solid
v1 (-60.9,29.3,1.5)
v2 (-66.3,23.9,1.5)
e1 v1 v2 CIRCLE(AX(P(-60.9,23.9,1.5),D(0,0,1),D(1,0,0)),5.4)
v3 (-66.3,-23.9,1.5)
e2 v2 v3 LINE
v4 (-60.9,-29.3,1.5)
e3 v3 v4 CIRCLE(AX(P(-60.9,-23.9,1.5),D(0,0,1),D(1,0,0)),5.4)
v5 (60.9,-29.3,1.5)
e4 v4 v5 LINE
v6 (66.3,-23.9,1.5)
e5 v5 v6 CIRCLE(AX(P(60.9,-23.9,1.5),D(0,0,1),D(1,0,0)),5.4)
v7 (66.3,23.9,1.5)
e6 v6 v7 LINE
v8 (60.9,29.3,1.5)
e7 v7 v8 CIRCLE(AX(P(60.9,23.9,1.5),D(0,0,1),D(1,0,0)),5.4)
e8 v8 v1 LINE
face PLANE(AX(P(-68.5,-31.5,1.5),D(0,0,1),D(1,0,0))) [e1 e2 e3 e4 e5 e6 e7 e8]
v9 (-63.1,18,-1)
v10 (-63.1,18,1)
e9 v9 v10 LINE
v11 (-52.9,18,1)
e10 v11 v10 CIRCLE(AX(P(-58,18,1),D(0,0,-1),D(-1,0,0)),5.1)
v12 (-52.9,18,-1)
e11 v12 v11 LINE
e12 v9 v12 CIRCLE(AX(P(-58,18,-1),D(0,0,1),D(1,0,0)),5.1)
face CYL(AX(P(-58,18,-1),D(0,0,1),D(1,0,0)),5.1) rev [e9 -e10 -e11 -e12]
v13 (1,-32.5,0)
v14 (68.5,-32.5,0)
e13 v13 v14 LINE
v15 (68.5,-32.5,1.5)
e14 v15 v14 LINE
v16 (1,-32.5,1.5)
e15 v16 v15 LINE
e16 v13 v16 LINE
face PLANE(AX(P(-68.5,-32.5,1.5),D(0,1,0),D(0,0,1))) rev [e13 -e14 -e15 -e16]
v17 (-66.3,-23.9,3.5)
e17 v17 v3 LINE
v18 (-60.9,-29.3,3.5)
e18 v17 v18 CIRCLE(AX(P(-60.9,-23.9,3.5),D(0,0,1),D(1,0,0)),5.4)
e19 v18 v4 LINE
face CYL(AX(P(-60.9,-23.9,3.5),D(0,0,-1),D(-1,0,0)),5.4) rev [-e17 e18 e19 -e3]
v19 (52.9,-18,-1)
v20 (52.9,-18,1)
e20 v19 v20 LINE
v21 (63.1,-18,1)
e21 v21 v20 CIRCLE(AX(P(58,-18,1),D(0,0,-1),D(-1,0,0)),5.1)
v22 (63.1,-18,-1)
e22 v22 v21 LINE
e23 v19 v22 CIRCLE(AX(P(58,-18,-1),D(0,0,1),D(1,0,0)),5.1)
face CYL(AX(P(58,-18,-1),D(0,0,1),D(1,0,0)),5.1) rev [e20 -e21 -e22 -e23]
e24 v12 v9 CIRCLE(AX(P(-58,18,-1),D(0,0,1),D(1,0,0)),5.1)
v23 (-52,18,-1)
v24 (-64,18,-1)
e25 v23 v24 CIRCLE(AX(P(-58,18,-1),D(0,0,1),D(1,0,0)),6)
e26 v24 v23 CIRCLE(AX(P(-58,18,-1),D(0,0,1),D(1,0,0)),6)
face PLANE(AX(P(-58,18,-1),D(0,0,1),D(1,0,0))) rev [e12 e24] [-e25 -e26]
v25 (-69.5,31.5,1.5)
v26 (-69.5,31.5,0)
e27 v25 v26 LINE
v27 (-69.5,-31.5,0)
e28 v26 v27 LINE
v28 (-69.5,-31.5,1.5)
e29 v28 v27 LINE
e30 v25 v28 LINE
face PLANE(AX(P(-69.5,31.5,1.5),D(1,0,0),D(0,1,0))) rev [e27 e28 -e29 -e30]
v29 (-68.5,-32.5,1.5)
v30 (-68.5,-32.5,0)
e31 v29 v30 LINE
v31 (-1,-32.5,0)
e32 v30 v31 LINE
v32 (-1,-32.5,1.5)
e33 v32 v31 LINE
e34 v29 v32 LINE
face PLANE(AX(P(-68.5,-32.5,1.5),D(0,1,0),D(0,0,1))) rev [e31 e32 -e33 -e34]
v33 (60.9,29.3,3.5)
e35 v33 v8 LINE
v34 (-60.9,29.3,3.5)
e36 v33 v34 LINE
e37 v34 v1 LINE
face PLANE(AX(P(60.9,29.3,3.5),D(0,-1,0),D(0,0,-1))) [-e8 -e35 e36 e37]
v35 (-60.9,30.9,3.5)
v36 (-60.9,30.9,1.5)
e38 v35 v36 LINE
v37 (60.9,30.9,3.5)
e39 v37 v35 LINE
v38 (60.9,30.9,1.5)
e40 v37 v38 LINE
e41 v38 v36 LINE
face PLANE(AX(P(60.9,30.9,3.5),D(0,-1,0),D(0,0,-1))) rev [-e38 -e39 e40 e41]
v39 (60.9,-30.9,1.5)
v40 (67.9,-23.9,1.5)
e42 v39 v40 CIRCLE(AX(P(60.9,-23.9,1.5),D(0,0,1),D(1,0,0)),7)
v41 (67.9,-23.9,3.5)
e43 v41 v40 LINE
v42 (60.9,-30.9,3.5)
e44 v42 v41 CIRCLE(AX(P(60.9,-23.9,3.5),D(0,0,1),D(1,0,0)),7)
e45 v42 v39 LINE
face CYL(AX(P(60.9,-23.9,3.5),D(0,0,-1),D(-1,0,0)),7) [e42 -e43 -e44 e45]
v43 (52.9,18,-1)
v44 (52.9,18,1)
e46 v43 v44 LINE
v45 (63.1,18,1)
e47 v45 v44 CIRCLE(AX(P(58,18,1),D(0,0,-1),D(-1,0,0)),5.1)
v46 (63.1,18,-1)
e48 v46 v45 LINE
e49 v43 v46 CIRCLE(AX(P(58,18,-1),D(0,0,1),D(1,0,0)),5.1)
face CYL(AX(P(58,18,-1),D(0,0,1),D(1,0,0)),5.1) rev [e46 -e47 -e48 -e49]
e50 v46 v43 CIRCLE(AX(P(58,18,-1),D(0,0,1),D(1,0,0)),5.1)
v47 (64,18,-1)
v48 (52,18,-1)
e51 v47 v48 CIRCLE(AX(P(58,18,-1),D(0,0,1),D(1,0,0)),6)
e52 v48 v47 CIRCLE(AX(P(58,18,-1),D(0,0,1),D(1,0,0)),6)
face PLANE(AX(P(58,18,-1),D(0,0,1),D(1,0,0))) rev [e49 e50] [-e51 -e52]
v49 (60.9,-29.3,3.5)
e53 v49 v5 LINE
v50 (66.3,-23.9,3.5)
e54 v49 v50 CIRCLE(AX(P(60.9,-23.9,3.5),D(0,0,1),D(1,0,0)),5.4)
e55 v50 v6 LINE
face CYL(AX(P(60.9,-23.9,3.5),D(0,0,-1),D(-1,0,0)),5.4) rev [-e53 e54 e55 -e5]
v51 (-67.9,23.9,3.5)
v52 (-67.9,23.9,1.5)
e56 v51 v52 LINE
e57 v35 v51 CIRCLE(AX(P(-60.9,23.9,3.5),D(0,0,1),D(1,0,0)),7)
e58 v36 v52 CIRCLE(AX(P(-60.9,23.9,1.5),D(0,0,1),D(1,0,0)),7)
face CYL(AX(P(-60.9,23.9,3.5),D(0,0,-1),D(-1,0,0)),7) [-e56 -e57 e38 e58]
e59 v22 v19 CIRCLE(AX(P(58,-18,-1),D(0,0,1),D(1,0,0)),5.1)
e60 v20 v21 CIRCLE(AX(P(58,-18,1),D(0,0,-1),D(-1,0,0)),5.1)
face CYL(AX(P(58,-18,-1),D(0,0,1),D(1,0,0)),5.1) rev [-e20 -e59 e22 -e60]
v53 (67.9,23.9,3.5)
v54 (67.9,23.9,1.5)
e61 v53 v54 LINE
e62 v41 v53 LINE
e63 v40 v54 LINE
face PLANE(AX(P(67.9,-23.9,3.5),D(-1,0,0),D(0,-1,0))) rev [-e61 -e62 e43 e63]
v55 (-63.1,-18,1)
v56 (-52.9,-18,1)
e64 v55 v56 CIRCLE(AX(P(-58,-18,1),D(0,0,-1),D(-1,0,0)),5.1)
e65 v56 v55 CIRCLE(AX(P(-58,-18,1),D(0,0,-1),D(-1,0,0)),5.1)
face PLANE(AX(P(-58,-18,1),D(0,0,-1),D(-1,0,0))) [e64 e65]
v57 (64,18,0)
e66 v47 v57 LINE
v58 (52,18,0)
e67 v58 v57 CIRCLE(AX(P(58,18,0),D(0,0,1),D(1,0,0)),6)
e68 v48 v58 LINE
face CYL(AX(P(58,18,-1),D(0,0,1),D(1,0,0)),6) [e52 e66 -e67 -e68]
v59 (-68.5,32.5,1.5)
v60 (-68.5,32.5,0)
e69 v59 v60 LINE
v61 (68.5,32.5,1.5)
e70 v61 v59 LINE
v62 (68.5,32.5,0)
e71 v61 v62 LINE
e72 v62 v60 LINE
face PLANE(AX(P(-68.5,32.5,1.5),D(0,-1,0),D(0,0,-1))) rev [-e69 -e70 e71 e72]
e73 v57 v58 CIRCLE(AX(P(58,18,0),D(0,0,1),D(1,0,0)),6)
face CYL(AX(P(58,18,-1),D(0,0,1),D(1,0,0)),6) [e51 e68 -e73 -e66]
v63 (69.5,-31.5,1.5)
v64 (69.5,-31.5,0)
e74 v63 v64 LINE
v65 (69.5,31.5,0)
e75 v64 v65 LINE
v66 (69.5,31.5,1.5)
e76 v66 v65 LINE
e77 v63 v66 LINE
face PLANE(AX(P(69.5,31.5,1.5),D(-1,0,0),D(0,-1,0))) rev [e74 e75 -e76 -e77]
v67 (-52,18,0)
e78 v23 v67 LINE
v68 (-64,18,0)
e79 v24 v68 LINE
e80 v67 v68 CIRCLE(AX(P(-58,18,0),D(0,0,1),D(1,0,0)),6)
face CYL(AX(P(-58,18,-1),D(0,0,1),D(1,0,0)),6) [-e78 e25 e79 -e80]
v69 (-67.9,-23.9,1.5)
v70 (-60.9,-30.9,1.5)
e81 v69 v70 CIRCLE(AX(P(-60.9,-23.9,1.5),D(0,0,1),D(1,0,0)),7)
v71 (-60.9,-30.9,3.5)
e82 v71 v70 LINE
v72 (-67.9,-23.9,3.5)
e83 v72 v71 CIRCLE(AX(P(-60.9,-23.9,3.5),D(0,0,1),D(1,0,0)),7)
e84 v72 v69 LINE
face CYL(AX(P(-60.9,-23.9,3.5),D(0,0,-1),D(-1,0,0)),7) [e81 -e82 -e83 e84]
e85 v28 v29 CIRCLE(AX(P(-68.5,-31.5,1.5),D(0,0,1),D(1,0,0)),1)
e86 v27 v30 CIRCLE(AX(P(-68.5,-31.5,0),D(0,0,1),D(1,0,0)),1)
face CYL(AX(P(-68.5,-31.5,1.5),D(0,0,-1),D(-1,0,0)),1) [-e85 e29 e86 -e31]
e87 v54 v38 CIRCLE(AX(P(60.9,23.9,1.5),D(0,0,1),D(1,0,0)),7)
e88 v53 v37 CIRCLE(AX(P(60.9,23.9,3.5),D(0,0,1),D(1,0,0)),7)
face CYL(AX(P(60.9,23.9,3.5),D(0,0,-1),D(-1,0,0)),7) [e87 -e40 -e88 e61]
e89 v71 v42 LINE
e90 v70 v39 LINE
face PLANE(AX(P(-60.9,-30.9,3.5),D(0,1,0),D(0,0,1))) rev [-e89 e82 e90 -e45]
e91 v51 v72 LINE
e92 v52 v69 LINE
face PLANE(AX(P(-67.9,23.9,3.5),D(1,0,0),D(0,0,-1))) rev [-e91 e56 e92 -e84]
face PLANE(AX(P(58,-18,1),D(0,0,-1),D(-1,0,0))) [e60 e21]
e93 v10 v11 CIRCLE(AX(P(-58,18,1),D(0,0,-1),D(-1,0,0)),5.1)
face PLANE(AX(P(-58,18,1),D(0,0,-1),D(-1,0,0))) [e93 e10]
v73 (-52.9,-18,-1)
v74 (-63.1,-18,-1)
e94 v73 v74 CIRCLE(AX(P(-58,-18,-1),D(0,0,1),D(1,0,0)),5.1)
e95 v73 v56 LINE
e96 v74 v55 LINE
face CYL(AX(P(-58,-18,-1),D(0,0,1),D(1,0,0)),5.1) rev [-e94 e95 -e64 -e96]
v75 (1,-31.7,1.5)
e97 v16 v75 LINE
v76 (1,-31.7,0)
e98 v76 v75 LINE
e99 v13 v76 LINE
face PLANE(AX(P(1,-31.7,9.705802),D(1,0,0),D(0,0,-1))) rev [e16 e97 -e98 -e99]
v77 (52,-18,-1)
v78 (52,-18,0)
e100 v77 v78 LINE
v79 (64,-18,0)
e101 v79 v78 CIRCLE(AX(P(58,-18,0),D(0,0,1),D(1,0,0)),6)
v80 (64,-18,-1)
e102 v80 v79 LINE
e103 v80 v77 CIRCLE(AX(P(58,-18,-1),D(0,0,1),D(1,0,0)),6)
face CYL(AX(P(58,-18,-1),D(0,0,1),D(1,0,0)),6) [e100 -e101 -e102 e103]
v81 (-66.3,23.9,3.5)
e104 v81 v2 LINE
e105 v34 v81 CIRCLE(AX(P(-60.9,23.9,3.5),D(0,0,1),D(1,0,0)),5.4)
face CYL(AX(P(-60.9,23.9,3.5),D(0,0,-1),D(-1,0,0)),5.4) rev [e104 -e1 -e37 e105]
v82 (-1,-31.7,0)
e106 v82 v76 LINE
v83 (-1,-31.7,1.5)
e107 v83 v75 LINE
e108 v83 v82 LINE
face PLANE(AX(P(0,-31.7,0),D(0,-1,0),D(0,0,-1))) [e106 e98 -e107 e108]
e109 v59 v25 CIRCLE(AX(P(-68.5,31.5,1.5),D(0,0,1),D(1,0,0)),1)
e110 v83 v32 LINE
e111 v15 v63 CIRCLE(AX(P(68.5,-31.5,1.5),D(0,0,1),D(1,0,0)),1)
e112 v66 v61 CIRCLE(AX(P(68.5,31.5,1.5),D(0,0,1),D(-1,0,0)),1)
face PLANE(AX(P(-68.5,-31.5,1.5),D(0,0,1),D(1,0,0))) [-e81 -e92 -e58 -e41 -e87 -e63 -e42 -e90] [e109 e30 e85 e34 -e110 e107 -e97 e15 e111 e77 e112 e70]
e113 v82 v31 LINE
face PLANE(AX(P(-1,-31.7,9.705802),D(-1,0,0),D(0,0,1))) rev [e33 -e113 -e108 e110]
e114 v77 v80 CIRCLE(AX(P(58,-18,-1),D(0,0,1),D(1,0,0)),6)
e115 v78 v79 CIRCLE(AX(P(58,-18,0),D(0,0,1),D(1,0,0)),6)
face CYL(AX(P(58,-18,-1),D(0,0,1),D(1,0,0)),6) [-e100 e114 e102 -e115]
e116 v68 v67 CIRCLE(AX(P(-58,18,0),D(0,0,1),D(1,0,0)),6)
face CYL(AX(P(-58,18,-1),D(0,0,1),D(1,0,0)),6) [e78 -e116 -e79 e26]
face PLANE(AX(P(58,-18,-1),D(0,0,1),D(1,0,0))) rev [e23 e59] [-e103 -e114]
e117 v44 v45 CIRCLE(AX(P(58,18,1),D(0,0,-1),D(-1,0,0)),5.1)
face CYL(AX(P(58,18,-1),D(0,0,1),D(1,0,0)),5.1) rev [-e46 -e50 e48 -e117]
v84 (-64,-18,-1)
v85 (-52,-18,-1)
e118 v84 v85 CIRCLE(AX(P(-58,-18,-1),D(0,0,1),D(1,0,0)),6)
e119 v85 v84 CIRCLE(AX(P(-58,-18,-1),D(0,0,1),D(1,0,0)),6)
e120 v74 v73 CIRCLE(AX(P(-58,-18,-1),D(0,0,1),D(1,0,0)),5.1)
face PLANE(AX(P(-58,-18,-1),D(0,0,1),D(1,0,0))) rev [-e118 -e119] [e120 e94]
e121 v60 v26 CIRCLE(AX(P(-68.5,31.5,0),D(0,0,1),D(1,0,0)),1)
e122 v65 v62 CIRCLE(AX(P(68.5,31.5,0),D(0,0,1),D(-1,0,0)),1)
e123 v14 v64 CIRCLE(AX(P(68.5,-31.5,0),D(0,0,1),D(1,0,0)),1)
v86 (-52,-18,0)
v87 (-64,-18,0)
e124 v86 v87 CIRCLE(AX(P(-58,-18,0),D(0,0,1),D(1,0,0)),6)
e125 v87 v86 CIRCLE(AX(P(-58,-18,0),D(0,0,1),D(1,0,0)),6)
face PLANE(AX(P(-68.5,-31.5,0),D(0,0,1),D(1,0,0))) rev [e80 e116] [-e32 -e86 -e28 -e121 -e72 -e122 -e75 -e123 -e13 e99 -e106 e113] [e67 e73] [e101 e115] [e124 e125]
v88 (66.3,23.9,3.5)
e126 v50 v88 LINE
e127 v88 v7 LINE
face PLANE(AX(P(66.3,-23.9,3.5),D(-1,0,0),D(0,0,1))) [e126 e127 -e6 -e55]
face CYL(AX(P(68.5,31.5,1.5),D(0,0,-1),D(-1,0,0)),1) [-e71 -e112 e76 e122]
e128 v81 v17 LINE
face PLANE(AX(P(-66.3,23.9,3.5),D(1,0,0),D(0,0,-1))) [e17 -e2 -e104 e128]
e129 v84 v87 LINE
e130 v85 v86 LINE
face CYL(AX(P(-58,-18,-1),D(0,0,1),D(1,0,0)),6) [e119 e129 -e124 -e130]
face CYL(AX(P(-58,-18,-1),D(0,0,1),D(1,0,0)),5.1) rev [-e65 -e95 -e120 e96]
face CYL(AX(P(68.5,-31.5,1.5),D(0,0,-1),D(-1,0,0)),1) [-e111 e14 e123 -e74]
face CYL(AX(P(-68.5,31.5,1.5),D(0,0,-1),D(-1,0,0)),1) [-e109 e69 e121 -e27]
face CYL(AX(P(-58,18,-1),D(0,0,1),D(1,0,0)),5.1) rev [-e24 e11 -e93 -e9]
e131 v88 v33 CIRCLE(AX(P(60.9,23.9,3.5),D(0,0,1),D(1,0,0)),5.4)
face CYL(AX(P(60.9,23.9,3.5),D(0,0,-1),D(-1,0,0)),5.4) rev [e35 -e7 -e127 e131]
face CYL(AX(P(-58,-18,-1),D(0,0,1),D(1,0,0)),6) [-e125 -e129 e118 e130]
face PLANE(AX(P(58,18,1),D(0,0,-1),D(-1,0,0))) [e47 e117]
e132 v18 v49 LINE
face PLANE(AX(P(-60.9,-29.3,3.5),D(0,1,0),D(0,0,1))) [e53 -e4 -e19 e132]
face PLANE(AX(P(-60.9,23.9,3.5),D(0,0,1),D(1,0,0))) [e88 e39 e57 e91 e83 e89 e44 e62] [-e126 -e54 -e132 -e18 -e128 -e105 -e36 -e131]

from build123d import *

# Parameters (mm, degrees)
BOSS_EXTRUDE1_DEPTH = 1.5
BOSS_EXTRUDE2_START = -1.5
SKETCH2_R           = 6
SKETCH2_R_2         = 5.1
BOSS_EXTRUDE2_DEPTH = 1
BOSS_EXTRUDE3_DEPTH = 2
SKETCH7_W           = 2
SKETCH7_H           = 19.411603012
CUT_EXTRUDE3_DEPTH  = 0.8
CUT_EXTRUDE4_START  = -1
SKETCH8_R           = 5.1
CUT_EXTRUDE4_DEPTH  = 1


with BuildPart() as part:
    # Sketch1 → Boss-Extrude1 (new body)
    with BuildSketch(Plane.XY):
        with BuildLine():
            Line((-68.5, 32.5), (68.5, 32.5))
            ThreePointArc((68.5, 32.5), (69.207106781, 32.207106781), (69.5, 31.5))
            Line((69.5, 31.5), (69.5, -31.5))
            ThreePointArc((69.5, -31.5), (69.207106781, -32.207106781), (68.5, -32.5))
            Line((68.5, -32.5), (-68.5, -32.5))
            ThreePointArc((-68.5, -32.5), (-69.207106781, -32.207106781), (-69.5, -31.5))
            Line((-69.5, -31.5), (-69.5, 31.5))
            ThreePointArc((-69.5, 31.5), (-69.207106781, 32.207106781), (-68.5, 32.5))
        make_face()
    extrude(amount=BOSS_EXTRUDE1_DEPTH)

    # Sketch2 → Boss-Extrude2 (add)
    # profile 1 of 4: a face of its own
    with BuildSketch(Plane.XY.offset(1.5).offset(BOSS_EXTRUDE2_START)):
        with Locations((-58, 18)):
            Circle(SKETCH2_R)
        with Locations((-58, 18)):
            Circle(SKETCH2_R_2, mode=Mode.SUBTRACT)
    # profile 2 of 4: a face of its own
    with BuildSketch(Plane.XY.offset(1.5).offset(BOSS_EXTRUDE2_START)):
        with Locations((58, 18)):
            Circle(SKETCH2_R)
        with Locations((58, 18)):
            Circle(SKETCH2_R_2, mode=Mode.SUBTRACT)
    # profile 3 of 4: a face of its own
    with BuildSketch(Plane.XY.offset(1.5).offset(BOSS_EXTRUDE2_START)):
        with Locations((-58, -18)):
            Circle(SKETCH2_R)
        with Locations((-58, -18)):
            Circle(SKETCH2_R_2, mode=Mode.SUBTRACT)
    # profile 4 of 4: a face of its own
    with BuildSketch(Plane.XY.offset(1.5).offset(BOSS_EXTRUDE2_START)):
        with Locations((58, -18)):
            Circle(SKETCH2_R)
        with Locations((58, -18)):
            Circle(SKETCH2_R_2, mode=Mode.SUBTRACT)
    extrude(amount=-BOSS_EXTRUDE2_DEPTH)

    # Sketch3 → Boss-Extrude3 (add)
    with BuildSketch(Plane.XY.offset(1.5)):
        with BuildLine():
            Line((60.9, 30.9), (-60.9, 30.9))
            ThreePointArc((-60.9, 30.9), (-65.849747468, 28.849747468), (-67.9, 23.9))
            Line((-67.9, 23.9), (-67.9, -23.9))
            ThreePointArc((-67.9, -23.9), (-65.849747468, -28.849747468), (-60.9, -30.9))
            Line((-60.9, -30.9), (60.9, -30.9))
            ThreePointArc((60.9, -30.9), (65.849747468, -28.849747468), (67.9, -23.9))
            Line((67.9, -23.9), (67.9, 23.9))
            ThreePointArc((67.9, 23.9), (65.849747468, 28.849747468), (60.9, 30.9))
        make_face()
        with BuildLine():
            Line((60.9, 29.3), (-60.9, 29.3))
            ThreePointArc((-60.9, 29.3), (-64.718376618, 27.718376618), (-66.3, 23.9))
            Line((-66.3, 23.9), (-66.3, -23.9))
            ThreePointArc((-66.3, -23.9), (-64.718376618, -27.718376618), (-60.9, -29.3))
            Line((-60.9, -29.3), (60.9, -29.3))
            ThreePointArc((60.9, -29.3), (64.718376618, -27.718376618), (66.3, -23.9))
            Line((66.3, -23.9), (66.3, 23.9))
            ThreePointArc((66.3, 23.9), (64.718376618, 27.718376618), (60.9, 29.3))
        make_face(mode=Mode.SUBTRACT)
    extrude(amount=BOSS_EXTRUDE3_DEPTH)

    # Sketch7 → Cut-Extrude3 (cut)
    with BuildSketch(Plane(origin=(0, -32.5, 0), x_dir=(-1, 0, 0), z_dir=(0, -1, 0))):
        Rectangle(SKETCH7_W, SKETCH7_H)
    extrude(amount=-CUT_EXTRUDE3_DEPTH, mode=Mode.SUBTRACT)

    # Sketch8 → Cut-Extrude4 (cut)
    with BuildSketch(Plane(origin=(0, 0, 0), x_dir=(-1, 0, 0), z_dir=(0, 0, -1)).offset(CUT_EXTRUDE4_START)):
        with Locations(Location((-58, 18, 0), (0, 0, 180))):
            Circle(SKETCH8_R)
        with Locations(Location((58, 18, 0), (0, 0, 180))):
            Circle(SKETCH8_R)
        with Locations(Location((58, -18, 0), (0, 0, 180))):
            Circle(SKETCH8_R)
        with Locations(Location((-58, -18, 0), (0, 0, 180))):
            Circle(SKETCH8_R)
    extrude(amount=CUT_EXTRUDE4_DEPTH, mode=Mode.SUBTRACT)


solid = part.part
